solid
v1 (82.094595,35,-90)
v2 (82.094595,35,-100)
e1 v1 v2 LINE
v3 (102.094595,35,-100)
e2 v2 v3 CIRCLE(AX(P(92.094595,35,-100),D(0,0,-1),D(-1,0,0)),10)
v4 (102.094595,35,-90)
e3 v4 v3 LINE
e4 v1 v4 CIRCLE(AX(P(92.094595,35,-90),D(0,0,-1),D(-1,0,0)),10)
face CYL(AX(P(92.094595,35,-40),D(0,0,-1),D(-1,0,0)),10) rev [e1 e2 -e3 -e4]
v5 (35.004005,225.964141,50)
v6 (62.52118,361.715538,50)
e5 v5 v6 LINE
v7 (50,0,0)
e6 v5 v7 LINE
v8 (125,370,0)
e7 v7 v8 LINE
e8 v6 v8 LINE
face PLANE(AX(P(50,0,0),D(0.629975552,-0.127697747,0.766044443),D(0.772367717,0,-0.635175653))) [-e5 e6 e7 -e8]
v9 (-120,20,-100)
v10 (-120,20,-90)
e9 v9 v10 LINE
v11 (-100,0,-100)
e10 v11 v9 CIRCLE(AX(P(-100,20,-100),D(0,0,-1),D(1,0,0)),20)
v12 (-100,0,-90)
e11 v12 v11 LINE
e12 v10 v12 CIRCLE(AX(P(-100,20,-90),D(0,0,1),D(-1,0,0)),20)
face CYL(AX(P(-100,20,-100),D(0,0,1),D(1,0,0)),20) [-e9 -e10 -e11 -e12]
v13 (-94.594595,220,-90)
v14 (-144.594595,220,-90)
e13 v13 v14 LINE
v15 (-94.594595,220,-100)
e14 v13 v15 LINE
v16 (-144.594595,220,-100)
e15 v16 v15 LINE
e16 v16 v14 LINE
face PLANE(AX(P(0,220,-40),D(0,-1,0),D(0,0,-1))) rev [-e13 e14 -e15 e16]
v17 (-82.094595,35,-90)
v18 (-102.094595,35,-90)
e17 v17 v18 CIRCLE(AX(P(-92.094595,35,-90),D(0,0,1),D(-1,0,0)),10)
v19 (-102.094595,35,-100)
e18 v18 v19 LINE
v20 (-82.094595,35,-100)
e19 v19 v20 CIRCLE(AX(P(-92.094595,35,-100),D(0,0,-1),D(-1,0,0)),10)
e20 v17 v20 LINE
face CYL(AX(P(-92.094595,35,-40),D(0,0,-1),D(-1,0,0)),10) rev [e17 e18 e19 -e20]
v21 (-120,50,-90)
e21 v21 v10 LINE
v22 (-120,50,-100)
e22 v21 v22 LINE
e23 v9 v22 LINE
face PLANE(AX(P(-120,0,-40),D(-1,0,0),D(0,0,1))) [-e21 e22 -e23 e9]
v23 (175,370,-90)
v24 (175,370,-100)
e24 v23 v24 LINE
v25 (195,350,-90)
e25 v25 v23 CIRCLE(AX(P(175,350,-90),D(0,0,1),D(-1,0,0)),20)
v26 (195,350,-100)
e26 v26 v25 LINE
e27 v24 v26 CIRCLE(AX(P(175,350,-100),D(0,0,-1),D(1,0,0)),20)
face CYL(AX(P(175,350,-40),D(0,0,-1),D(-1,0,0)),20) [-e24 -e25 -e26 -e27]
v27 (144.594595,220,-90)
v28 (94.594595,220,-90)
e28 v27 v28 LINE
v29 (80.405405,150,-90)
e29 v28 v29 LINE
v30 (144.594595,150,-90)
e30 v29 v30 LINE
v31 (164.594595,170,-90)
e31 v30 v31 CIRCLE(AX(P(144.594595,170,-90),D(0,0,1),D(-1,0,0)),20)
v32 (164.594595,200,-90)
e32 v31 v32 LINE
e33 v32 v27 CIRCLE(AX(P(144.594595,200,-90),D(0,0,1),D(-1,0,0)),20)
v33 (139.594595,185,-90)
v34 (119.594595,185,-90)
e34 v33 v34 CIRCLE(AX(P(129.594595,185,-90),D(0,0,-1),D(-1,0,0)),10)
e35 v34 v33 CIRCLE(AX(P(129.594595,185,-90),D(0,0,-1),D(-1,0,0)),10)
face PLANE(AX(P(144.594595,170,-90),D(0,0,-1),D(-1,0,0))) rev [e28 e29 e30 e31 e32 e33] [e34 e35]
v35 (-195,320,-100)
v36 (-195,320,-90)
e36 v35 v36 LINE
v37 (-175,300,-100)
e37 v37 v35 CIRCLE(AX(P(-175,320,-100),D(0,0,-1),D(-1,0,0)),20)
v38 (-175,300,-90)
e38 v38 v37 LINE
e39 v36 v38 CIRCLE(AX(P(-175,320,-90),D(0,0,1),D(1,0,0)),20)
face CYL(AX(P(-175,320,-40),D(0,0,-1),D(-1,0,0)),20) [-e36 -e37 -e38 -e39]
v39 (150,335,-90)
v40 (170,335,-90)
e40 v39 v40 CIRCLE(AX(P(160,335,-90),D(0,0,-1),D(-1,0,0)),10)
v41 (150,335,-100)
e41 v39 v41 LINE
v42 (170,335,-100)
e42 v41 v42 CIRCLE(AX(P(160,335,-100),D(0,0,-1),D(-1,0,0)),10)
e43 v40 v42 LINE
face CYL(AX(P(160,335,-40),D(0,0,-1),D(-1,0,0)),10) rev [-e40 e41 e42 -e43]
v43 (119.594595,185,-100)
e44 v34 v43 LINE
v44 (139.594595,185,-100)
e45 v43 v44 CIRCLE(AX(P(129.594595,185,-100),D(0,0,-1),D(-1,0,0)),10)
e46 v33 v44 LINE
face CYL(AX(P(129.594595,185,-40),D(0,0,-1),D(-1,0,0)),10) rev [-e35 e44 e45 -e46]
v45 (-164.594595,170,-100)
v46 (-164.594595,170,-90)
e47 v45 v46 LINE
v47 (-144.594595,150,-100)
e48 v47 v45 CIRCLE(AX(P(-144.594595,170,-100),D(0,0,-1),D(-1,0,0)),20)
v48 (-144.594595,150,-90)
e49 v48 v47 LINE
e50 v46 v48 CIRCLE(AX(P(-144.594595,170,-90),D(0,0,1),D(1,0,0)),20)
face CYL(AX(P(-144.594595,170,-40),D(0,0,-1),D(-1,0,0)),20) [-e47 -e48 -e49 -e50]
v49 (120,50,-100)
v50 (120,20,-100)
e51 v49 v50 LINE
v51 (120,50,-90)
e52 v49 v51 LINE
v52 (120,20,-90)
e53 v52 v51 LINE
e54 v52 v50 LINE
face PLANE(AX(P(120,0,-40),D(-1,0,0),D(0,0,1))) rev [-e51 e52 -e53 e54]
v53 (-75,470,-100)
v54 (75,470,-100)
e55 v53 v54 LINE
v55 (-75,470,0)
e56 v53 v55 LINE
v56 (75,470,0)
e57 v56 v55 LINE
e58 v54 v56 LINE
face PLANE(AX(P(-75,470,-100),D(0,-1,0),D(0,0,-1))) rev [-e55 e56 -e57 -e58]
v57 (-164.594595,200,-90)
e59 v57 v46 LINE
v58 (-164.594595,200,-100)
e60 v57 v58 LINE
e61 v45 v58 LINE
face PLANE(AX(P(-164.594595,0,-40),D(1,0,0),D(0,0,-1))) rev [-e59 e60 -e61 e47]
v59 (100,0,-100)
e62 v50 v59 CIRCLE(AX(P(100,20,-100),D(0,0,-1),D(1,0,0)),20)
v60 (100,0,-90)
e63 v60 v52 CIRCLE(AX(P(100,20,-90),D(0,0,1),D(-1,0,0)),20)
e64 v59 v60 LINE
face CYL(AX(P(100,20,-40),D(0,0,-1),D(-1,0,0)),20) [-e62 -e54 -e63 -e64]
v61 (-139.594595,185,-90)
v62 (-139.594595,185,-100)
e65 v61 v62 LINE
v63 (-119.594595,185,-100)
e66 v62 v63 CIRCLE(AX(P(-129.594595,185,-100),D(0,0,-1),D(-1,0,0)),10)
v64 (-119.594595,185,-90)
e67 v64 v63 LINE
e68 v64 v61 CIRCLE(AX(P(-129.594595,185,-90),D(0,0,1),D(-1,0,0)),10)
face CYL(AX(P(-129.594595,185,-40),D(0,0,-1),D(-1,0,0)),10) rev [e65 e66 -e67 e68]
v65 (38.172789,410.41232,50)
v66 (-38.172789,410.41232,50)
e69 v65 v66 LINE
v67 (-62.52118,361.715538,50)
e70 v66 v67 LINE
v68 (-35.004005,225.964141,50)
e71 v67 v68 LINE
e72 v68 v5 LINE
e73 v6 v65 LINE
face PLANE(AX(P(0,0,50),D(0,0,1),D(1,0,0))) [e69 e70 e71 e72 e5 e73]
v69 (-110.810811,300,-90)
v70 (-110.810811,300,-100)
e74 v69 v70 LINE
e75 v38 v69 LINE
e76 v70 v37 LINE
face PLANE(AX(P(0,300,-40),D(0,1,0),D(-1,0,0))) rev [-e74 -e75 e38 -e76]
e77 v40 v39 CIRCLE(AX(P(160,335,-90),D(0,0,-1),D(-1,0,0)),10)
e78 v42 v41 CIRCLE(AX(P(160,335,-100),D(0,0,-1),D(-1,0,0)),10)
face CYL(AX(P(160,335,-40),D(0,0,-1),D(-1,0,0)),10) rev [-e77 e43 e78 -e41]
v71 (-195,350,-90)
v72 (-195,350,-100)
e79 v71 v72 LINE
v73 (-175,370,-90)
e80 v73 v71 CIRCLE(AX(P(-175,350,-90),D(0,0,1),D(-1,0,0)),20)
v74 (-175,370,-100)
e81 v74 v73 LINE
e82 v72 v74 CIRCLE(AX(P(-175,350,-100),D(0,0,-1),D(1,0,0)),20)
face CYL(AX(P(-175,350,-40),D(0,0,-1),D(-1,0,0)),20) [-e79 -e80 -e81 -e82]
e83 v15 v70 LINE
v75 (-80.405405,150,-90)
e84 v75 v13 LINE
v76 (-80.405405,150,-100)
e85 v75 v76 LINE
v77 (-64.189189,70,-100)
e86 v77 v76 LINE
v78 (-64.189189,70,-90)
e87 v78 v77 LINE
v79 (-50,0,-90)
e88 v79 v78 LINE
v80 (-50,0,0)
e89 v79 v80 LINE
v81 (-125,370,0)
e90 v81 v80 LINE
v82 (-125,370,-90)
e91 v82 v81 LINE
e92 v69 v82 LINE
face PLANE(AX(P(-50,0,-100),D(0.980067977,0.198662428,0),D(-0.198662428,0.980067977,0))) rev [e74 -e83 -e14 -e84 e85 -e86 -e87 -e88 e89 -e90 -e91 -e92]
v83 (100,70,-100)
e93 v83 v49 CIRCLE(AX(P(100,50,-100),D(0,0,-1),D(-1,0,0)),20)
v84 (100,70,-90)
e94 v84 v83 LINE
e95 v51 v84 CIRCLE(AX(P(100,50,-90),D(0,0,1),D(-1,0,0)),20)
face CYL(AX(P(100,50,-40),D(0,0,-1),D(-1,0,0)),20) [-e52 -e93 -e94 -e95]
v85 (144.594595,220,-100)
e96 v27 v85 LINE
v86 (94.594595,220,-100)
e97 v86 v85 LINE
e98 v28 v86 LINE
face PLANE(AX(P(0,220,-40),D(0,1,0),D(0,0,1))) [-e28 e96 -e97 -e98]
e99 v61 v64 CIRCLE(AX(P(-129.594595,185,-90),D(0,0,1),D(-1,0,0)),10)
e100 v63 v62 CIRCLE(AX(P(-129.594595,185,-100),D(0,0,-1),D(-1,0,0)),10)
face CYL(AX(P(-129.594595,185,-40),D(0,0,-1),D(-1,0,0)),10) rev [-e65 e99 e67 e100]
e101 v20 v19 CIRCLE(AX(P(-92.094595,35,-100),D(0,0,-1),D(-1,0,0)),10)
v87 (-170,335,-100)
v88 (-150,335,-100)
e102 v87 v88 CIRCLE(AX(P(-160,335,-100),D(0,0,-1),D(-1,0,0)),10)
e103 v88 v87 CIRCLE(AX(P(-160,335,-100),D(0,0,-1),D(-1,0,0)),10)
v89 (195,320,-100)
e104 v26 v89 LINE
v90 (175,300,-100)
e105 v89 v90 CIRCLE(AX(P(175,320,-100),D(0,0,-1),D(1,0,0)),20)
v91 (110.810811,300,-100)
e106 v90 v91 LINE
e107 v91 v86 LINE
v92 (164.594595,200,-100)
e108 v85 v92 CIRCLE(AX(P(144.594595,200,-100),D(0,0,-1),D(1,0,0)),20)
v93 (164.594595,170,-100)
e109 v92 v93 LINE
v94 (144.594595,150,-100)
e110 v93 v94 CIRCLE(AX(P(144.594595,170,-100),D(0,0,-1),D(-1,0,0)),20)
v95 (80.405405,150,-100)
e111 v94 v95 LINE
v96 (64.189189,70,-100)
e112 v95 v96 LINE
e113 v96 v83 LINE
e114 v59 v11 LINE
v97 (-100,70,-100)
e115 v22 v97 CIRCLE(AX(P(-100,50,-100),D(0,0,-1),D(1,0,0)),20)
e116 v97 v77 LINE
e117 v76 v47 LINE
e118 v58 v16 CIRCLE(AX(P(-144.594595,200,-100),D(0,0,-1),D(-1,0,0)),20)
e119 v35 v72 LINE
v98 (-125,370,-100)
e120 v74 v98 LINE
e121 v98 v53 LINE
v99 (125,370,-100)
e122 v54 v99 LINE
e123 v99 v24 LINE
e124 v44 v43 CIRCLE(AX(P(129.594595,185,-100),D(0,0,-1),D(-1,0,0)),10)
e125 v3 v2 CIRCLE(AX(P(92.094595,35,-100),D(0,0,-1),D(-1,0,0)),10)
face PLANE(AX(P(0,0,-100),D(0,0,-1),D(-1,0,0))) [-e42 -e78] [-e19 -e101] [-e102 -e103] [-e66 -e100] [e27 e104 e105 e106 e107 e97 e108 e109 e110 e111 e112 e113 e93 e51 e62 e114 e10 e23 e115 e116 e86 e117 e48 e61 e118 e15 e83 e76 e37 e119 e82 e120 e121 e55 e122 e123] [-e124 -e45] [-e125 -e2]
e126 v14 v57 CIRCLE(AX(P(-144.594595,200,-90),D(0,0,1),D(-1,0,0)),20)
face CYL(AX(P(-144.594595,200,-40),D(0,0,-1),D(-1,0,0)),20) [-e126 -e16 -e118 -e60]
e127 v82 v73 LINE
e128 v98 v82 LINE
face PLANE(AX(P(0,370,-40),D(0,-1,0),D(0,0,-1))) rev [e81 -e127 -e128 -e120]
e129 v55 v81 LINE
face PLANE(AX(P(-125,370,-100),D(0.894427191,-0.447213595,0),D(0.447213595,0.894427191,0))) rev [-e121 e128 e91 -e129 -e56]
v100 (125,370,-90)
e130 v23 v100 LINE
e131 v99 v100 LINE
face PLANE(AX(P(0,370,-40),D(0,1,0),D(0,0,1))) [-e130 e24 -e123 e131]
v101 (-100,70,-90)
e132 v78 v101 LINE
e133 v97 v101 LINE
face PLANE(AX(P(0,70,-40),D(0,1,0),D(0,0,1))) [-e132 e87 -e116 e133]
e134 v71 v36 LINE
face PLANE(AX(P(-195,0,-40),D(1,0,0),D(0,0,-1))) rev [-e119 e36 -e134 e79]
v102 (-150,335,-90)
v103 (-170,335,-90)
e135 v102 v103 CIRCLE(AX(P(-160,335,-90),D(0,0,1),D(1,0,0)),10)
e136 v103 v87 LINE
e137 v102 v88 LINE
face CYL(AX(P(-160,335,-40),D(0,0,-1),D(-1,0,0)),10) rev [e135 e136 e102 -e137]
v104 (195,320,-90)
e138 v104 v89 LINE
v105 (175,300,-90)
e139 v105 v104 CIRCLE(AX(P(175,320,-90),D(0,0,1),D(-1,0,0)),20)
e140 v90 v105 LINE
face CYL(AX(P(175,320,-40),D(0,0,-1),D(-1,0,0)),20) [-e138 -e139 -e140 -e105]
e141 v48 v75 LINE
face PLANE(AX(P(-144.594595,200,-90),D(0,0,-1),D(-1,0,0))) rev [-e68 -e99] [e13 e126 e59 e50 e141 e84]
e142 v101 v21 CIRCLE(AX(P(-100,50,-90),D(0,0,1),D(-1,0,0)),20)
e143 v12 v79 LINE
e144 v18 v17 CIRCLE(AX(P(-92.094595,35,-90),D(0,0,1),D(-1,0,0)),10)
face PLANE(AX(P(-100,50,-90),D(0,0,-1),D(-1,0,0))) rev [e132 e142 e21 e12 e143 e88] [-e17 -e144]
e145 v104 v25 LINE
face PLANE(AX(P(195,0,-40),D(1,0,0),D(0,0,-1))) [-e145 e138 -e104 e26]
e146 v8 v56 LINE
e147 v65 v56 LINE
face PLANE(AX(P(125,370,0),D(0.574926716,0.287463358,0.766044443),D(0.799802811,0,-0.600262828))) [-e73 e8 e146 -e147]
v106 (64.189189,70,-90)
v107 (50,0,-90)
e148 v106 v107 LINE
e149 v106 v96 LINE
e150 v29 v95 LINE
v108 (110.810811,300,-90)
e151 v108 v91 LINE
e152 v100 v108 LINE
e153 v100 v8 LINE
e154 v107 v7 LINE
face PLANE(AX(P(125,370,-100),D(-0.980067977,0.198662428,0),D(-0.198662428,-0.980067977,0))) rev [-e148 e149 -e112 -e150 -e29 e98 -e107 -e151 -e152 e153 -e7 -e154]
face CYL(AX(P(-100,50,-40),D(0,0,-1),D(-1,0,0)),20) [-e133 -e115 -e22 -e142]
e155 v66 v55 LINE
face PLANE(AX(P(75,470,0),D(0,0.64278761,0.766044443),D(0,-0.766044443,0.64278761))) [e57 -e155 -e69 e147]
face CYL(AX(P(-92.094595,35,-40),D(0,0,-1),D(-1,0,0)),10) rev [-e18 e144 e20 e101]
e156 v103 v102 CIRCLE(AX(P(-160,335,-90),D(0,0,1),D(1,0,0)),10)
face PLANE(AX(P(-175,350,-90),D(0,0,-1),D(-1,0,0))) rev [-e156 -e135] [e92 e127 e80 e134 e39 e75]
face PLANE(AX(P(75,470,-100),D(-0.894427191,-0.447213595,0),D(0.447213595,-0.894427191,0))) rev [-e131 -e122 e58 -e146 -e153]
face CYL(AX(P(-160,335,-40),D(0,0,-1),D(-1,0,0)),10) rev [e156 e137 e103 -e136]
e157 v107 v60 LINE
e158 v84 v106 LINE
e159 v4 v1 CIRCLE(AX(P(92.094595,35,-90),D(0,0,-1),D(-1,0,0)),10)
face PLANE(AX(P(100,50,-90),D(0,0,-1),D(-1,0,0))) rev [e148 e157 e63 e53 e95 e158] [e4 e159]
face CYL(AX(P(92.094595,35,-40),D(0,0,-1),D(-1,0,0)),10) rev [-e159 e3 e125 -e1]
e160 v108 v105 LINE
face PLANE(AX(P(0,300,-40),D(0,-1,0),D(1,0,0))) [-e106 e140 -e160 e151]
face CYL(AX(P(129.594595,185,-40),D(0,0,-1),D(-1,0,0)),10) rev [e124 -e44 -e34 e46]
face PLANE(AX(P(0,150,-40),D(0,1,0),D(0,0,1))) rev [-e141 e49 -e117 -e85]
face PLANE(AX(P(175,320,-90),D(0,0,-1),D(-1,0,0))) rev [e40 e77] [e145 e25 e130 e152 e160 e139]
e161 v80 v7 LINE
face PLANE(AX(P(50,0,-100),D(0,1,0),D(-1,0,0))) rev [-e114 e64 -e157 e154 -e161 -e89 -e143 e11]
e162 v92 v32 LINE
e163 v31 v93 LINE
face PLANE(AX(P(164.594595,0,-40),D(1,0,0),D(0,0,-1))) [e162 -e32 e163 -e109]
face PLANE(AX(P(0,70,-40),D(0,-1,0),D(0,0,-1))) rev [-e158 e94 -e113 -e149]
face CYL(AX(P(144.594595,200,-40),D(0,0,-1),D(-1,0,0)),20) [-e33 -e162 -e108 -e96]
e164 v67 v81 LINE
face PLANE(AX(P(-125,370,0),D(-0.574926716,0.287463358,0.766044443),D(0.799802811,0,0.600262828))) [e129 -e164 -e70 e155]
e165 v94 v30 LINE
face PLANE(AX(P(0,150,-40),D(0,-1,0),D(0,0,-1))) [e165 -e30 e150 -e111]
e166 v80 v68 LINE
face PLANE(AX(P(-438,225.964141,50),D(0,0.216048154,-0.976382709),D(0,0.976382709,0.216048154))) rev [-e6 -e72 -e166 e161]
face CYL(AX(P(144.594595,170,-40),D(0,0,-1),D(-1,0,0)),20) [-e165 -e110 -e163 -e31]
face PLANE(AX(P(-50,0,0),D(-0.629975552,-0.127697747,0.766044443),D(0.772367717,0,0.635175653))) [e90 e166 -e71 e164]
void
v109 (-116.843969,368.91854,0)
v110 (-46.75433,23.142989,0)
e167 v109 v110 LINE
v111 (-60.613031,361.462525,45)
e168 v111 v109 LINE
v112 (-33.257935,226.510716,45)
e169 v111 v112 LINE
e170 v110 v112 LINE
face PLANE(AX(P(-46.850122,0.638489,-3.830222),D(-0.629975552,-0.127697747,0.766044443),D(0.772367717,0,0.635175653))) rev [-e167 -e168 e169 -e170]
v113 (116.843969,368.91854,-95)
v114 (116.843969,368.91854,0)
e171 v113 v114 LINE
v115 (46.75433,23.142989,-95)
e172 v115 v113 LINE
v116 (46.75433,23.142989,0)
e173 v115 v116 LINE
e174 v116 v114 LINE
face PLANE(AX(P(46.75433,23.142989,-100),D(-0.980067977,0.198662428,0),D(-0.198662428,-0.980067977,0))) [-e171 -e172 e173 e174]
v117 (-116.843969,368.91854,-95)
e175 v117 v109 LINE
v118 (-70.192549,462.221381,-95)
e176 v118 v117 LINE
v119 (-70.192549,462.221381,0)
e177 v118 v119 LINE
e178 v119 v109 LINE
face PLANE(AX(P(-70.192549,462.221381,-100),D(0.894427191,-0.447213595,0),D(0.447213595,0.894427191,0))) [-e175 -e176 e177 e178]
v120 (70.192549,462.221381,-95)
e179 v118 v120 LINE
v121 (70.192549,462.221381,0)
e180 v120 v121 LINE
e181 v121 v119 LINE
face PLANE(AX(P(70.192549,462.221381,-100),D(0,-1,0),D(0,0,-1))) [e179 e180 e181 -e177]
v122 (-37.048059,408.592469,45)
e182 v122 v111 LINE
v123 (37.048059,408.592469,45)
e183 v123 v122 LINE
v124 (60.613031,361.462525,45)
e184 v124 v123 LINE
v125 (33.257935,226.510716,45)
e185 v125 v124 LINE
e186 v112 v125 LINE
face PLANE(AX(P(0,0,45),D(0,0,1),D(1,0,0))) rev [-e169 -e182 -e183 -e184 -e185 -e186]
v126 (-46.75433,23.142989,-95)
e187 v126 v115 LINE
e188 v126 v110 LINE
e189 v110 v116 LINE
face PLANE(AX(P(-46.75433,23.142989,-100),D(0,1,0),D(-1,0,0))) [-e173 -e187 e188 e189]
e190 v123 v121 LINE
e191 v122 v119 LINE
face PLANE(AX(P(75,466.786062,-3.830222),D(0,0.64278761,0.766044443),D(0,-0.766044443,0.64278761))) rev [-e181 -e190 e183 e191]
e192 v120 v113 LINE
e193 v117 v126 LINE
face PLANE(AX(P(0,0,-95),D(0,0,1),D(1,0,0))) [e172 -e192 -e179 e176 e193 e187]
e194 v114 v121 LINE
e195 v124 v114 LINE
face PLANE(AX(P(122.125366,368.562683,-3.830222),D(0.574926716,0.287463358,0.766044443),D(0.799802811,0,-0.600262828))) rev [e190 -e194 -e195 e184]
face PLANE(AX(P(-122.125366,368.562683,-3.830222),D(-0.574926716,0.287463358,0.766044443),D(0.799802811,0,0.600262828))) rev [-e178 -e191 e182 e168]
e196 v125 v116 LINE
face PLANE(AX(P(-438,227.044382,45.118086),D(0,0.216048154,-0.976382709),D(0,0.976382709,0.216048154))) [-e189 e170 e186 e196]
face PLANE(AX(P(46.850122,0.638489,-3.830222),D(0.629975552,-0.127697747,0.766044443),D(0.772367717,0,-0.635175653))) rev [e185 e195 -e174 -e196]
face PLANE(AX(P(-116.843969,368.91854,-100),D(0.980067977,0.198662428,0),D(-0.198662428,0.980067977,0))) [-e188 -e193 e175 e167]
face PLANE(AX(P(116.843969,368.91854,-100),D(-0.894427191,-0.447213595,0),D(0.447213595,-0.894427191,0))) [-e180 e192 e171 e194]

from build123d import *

# Parameters (mm, degrees)
BOSS_EXTRUDE1_DEPTH  = 50
BOSS_EXTRUDE1_TAPER  = 50
CUT_EXTRUDE2_DEPTH   = 438
SHELL1_T             = -5
BOSS_EXTRUDE2_DEPTH  = 100
BOSS_EXTRUDE3_DEPTH  = 5
SKETCH9_R            = 10
BOSS_EXTRUDE4_DEPTH  = 10
FILLET1_R            = 20
FILLET2_R            = 20
FILLET3_R            = 20
SKETCH19_R           = 10
BOSS_EXTRUDE6_DEPTH  = 50
SKETCH35_R           = 10
BOSS_EXTRUDE7_DEPTH  = 50
SKETCH36_R           = 10
BOSS_EXTRUDE8_DEPTH  = 50
SKETCH37_R           = 10
BOSS_EXTRUDE9_DEPTH  = 50
SKETCH38_R           = 10
BOSS_EXTRUDE10_DEPTH = 50
SKETCH39_R           = 10
BOSS_EXTRUDE11_DEPTH = 50
SKETCH45_R           = 10
CUT_EXTRUDE3_DEPTH   = 50
CUT_EXTRUDE4_DEPTH   = 50
CUT_EXTRUDE5_DEPTH   = 50
CUT_EXTRUDE6_DEPTH   = 50
CUT_EXTRUDE7_DEPTH   = 50
CUT_EXTRUDE8_DEPTH   = 50


with BuildPart() as part:
    # Sketch2 → Boss-Extrude1 (new body)
    with BuildSketch(Plane.XY):
        Polygon((-50, 0), (50, 0), (125, 370), (75, 470), (-75, 470), (-125, 370), align=None)
    extrude(amount=BOSS_EXTRUDE1_DEPTH, taper=BOSS_EXTRUDE1_TAPER)

    # Sketch5 → Cut-Extrude2 (cut, symmetric)
    with BuildSketch(Plane(origin=(0, 0, 0), x_dir=(0, 0, -1), z_dir=(1, 0, 0))):
        Polygon((-50, 225.964141046), (0, 0), (-90.655287841, 0), align=None)
    extrude(amount=CUT_EXTRUDE2_DEPTH, both=True, mode=Mode.SUBTRACT)

    # Shell1
    shell1_openings = [part.faces().sort_by_distance(p)[0] for p in [
        (0, 259.665683382, 0),
    ]]
    offset(amount=SHELL1_T, openings=shell1_openings, kind=Kind.INTERSECTION)

    # Sketch6 → Boss-Extrude2 (add)
    with BuildSketch(Plane(origin=(0, 0, 0), x_dir=(-1, 0, 0), z_dir=(0, 0, -1))):
        Polygon((50, 0), (125, 370), (75, 470), (-75, 470), (-125, 370), (-50, 0), align=None)
        Polygon((-116.843969267, 368.91854031), (-70.192548989, 462.221380866), (70.192548989, 462.221380866), (116.843969267, 368.91854031), (46.754330446, 23.142988795), (-46.754330446, 23.142988795), align=None, mode=Mode.SUBTRACT)
    extrude(amount=BOSS_EXTRUDE2_DEPTH)

    # Sketch7 → Boss-Extrude3 (add)
    with BuildSketch(Plane(origin=(0, 0, -100), x_dir=(-1, 0, 0), z_dir=(0, 0, -1))):
        Polygon((-46.754330446, 23.142988795), (-116.843969267, 368.91854031), (-70.192548989, 462.221380866), (70.192548989, 462.221380866), (116.843969267, 368.91854031), (46.754330446, 23.142988795), align=None)
    extrude(amount=-BOSS_EXTRUDE3_DEPTH)

    # Sketch9 → Boss-Extrude4 (add)
    # profile 1 of 3: a face of its own
    with BuildSketch(Plane.XY.offset(-50)):
        Polygon((125, 370), (110.810810811, 300), (195, 300), (195, 370), align=None)
        with Locations((160, 335)):
            Circle(SKETCH9_R, mode=Mode.SUBTRACT)
    # profile 2 of 3: a face of its own
    with BuildSketch(Plane.XY.offset(-50)):
        Polygon((94.594594595, 220), (80.405405405, 150), (164.594594595, 150), (164.594594595, 220), align=None)
        with Locations((129.594594595, 185)):
            Circle(SKETCH9_R, mode=Mode.SUBTRACT)
    # profile 3 of 3: a face of its own
    with BuildSketch(Plane.XY.offset(-50)):
        Polygon((64.189189189, 70), (50, 0), (120, 0), (120, 70), align=None)
        with Locations((92.094594595, 35)):
            Circle(SKETCH9_R, mode=Mode.SUBTRACT)
    boss_extrude4 = extrude(amount=BOSS_EXTRUDE4_DEPTH)

    # Fillet1
    fillet1_edges = [part.edges().sort_by_distance(p)[0] for p in [
        (195, 300, -45),
        (195, 370, -45),
    ]]
    fillet(fillet1_edges, radius=FILLET1_R)

    # Fillet2
    fillet2_edges = [part.edges().sort_by_distance(p)[0] for p in [
        (164.594594595, 150, -45),
        (164.594594595, 220, -45),
        (120, 0, -45),
        (120, 70, -45),
    ]]
    fillet(fillet2_edges, radius=FILLET2_R)

    # Mirror1: Boss-Extrude4 across plane
    add(boss_extrude4.mirror(Plane(origin=(0, 0, 0), x_dir=(0, 0, 1), z_dir=(1, 0, 0))))

    # Fillet3
    fillet3_edges = [part.edges().sort_by_distance(p)[0] for p in [
        (-195, 300, -45),
        (-195, 370, -45),
        (-164.594594595, 150, -45),
        (-164.594594595, 220, -45),
        (-120, 70, -45),
        (-120, 0, -45),
    ]]
    fillet(fillet3_edges, radius=FILLET3_R)

    # Sketch19 → Boss-Extrude6 (add)
    with BuildSketch(Plane(origin=(0, 0, -50), x_dir=(-1, 0, 0), z_dir=(0, 0, -1))):
        with BuildLine():
            Line((94.594594595, 220), (80.405405405, 150))
            Line((80.405405405, 150), (144.594594595, 150))
            ThreePointArc((144.594594595, 150), (158.736730218, 155.857864376), (164.594594595, 170))
            Line((164.594594595, 170), (164.594594595, 200))
            ThreePointArc((164.594594595, 200), (158.736730218, 214.142135624), (144.594594595, 220))
            Line((144.594594595, 220), (94.594594595, 220))
        make_face()
        with Locations((129.594594595, 185)):
            Circle(SKETCH19_R, mode=Mode.SUBTRACT)
    extrude(amount=BOSS_EXTRUDE6_DEPTH)

    # Sketch35 → Boss-Extrude7 (add)
    with BuildSketch(Plane(origin=(0, 0, -50), x_dir=(-1, 0, 0), z_dir=(0, 0, -1))):
        with BuildLine():
            Line((110.810810811, 300), (175, 300))
            ThreePointArc((175, 300), (189.142135624, 305.857864376), (195, 320))
            Line((195, 320), (195, 350))
            ThreePointArc((195, 350), (189.142135624, 364.142135624), (175, 370))
            Line((175, 370), (125, 370))
            Line((125, 370), (110.810810811, 300))
        make_face()
        with Locations((160, 335)):
            Circle(SKETCH35_R, mode=Mode.SUBTRACT)
    extrude(amount=BOSS_EXTRUDE7_DEPTH)

    # Sketch36 → Boss-Extrude8 (add)
    with BuildSketch(Plane(origin=(0, 0, -50), x_dir=(-1, 0, 0), z_dir=(0, 0, -1))):
        with BuildLine():
            Line((64.189189189, 70), (50, 0))
            Line((50, 0), (100, 0))
            ThreePointArc((100, 0), (114.142135624, 5.857864376), (120, 20))
            Line((120, 20), (120, 50))
            ThreePointArc((120, 50), (114.142135624, 64.142135624), (100, 70))
            Line((100, 70), (64.189189189, 70))
        make_face()
        with Locations((92.094594595, 35)):
            Circle(SKETCH36_R, mode=Mode.SUBTRACT)
    extrude(amount=BOSS_EXTRUDE8_DEPTH)

    # Sketch37 → Boss-Extrude9 (add)
    with BuildSketch(Plane(origin=(0, 0, -50), x_dir=(-1, 0, 0), z_dir=(0, 0, -1))):
        with BuildLine():
            Line((-100, 70), (-64.189189189, 70))
            Line((-64.189189189, 70), (-50, 0))
            Line((-50, 0), (-100, 0))
            ThreePointArc((-100, 0), (-114.142135624, 5.857864376), (-120, 20))
            Line((-120, 20), (-120, 50))
            ThreePointArc((-120, 50), (-114.142135624, 64.142135624), (-100, 70))
        make_face()
        with Locations((-92.094594595, 35)):
            Circle(SKETCH37_R, mode=Mode.SUBTRACT)
    extrude(amount=BOSS_EXTRUDE9_DEPTH)

    # Sketch38 → Boss-Extrude10 (add)
    with BuildSketch(Plane(origin=(0, 0, -50), x_dir=(-1, 0, 0), z_dir=(0, 0, -1))):
        with BuildLine():
            Line((-144.594594595, 220), (-94.594594595, 220))
            Line((-94.594594595, 220), (-80.405405405, 150))
            Line((-80.405405405, 150), (-144.594594595, 150))
            ThreePointArc((-144.594594595, 150), (-158.736730218, 155.857864376), (-164.594594595, 170))
            Line((-164.594594595, 170), (-164.594594595, 200))
            ThreePointArc((-164.594594595, 200), (-158.736730218, 214.142135624), (-144.594594595, 220))
        make_face()
        with Locations((-129.594594595, 185)):
            Circle(SKETCH38_R, mode=Mode.SUBTRACT)
    extrude(amount=BOSS_EXTRUDE10_DEPTH)

    # Sketch39 → Boss-Extrude11 (add)
    with BuildSketch(Plane(origin=(0, 0, -50), x_dir=(-1, 0, 0), z_dir=(0, 0, -1))):
        with BuildLine():
            Line((-175, 370), (-125, 370))
            Line((-125, 370), (-110.810810811, 300))
            Line((-110.810810811, 300), (-175, 300))
            ThreePointArc((-175, 300), (-189.142135624, 305.857864376), (-195, 320))
            Line((-195, 320), (-195, 350))
            ThreePointArc((-195, 350), (-189.142135624, 364.142135624), (-175, 370))
        make_face()
        with Locations((-160, 335)):
            Circle(SKETCH39_R, mode=Mode.SUBTRACT)
    extrude(amount=BOSS_EXTRUDE11_DEPTH)

    # Sketch45 → Cut-Extrude3 (cut)
    with BuildSketch(Plane.XY.offset(-40)):
        with BuildLine():
            Line((-175, 370), (-125, 370))
            Line((-125, 370), (-110.810810811, 300))
            Line((-110.810810811, 300), (-175, 300))
            ThreePointArc((-175, 300), (-189.142135624, 305.857864376), (-195, 320))
            Line((-195, 320), (-195, 350))
            ThreePointArc((-195, 350), (-189.142135624, 364.142135624), (-175, 370))
        make_face()
        with Locations(Location((-160, 335, 0), (0, 0, 180))):
            Circle(SKETCH45_R, mode=Mode.SUBTRACT)
    extrude(amount=-CUT_EXTRUDE3_DEPTH, mode=Mode.SUBTRACT)

    # Sketch46 → Cut-Extrude4 (cut)
    with BuildSketch(Plane.XY.offset(-40)):
        with BuildLine():
            Line((-144.594594595, 220), (-94.594594595, 220))
            Line((-94.594594595, 220), (-80.405405405, 150))
            Line((-80.405405405, 150), (-144.594594595, 150))
            ThreePointArc((-144.594594595, 150), (-158.736730218, 155.857864376), (-164.594594595, 170))
            Line((-164.594594595, 170), (-164.594594595, 200))
            ThreePointArc((-164.594594595, 200), (-158.736730218, 214.142135624), (-144.594594595, 220))
        make_face()
    extrude(amount=-CUT_EXTRUDE4_DEPTH, mode=Mode.SUBTRACT)

    # Sketch47 → Cut-Extrude5 (cut)
    with BuildSketch(Plane.XY.offset(-40)):
        with BuildLine():
            Line((-100, 70), (-64.189189189, 70))
            Line((-64.189189189, 70), (-50, 0))
            Line((-50, 0), (-100, 0))
            ThreePointArc((-100, 0), (-114.142135624, 5.857864376), (-120, 20))
            Line((-120, 20), (-120, 50))
            ThreePointArc((-120, 50), (-114.142135624, 64.142135624), (-100, 70))
        make_face()
    extrude(amount=-CUT_EXTRUDE5_DEPTH, mode=Mode.SUBTRACT)

    # Sketch49 → Cut-Extrude6 (cut)
    with BuildSketch(Plane.XY.offset(-40)):
        with BuildLine():
            Line((125, 370), (175, 370))
            ThreePointArc((175, 370), (189.142135624, 364.142135624), (195, 350))
            Line((195, 350), (195, 320))
            ThreePointArc((195, 320), (189.142135624, 305.857864376), (175, 300))
            Line((175, 300), (110.810810811, 300))
            Line((110.810810811, 300), (125, 370))
        make_face()
    extrude(amount=-CUT_EXTRUDE6_DEPTH, mode=Mode.SUBTRACT)

    # Sketch50 → Cut-Extrude7 (cut)
    with BuildSketch(Plane.XY.offset(-40)):
        with BuildLine():
            Line((94.594594595, 220), (144.594594595, 220))
            ThreePointArc((144.594594595, 220), (158.736730218, 214.142135624), (164.594594595, 200))
            Line((164.594594595, 200), (164.594594595, 170))
            ThreePointArc((164.594594595, 170), (158.736730218, 155.857864376), (144.594594595, 150))
            Line((144.594594595, 150), (80.405405405, 150))
            Line((80.405405405, 150), (94.594594595, 220))
        make_face()
    extrude(amount=-CUT_EXTRUDE7_DEPTH, mode=Mode.SUBTRACT)

    # Sketch51 → Cut-Extrude8 (cut)
    with BuildSketch(Plane.XY.offset(-40)):
        with BuildLine():
            Line((100, 70), (64.189189189, 70))
            Line((64.189189189, 70), (50, 0))
            Line((50, 0), (100, 0))
            ThreePointArc((100, 0), (114.142135624, 5.857864376), (120, 20))
            Line((120, 20), (120, 50))
            ThreePointArc((120, 50), (114.142135624, 64.142135624), (100, 70))
        make_face()
    extrude(amount=-CUT_EXTRUDE8_DEPTH, mode=Mode.SUBTRACT)


solid = part.part
